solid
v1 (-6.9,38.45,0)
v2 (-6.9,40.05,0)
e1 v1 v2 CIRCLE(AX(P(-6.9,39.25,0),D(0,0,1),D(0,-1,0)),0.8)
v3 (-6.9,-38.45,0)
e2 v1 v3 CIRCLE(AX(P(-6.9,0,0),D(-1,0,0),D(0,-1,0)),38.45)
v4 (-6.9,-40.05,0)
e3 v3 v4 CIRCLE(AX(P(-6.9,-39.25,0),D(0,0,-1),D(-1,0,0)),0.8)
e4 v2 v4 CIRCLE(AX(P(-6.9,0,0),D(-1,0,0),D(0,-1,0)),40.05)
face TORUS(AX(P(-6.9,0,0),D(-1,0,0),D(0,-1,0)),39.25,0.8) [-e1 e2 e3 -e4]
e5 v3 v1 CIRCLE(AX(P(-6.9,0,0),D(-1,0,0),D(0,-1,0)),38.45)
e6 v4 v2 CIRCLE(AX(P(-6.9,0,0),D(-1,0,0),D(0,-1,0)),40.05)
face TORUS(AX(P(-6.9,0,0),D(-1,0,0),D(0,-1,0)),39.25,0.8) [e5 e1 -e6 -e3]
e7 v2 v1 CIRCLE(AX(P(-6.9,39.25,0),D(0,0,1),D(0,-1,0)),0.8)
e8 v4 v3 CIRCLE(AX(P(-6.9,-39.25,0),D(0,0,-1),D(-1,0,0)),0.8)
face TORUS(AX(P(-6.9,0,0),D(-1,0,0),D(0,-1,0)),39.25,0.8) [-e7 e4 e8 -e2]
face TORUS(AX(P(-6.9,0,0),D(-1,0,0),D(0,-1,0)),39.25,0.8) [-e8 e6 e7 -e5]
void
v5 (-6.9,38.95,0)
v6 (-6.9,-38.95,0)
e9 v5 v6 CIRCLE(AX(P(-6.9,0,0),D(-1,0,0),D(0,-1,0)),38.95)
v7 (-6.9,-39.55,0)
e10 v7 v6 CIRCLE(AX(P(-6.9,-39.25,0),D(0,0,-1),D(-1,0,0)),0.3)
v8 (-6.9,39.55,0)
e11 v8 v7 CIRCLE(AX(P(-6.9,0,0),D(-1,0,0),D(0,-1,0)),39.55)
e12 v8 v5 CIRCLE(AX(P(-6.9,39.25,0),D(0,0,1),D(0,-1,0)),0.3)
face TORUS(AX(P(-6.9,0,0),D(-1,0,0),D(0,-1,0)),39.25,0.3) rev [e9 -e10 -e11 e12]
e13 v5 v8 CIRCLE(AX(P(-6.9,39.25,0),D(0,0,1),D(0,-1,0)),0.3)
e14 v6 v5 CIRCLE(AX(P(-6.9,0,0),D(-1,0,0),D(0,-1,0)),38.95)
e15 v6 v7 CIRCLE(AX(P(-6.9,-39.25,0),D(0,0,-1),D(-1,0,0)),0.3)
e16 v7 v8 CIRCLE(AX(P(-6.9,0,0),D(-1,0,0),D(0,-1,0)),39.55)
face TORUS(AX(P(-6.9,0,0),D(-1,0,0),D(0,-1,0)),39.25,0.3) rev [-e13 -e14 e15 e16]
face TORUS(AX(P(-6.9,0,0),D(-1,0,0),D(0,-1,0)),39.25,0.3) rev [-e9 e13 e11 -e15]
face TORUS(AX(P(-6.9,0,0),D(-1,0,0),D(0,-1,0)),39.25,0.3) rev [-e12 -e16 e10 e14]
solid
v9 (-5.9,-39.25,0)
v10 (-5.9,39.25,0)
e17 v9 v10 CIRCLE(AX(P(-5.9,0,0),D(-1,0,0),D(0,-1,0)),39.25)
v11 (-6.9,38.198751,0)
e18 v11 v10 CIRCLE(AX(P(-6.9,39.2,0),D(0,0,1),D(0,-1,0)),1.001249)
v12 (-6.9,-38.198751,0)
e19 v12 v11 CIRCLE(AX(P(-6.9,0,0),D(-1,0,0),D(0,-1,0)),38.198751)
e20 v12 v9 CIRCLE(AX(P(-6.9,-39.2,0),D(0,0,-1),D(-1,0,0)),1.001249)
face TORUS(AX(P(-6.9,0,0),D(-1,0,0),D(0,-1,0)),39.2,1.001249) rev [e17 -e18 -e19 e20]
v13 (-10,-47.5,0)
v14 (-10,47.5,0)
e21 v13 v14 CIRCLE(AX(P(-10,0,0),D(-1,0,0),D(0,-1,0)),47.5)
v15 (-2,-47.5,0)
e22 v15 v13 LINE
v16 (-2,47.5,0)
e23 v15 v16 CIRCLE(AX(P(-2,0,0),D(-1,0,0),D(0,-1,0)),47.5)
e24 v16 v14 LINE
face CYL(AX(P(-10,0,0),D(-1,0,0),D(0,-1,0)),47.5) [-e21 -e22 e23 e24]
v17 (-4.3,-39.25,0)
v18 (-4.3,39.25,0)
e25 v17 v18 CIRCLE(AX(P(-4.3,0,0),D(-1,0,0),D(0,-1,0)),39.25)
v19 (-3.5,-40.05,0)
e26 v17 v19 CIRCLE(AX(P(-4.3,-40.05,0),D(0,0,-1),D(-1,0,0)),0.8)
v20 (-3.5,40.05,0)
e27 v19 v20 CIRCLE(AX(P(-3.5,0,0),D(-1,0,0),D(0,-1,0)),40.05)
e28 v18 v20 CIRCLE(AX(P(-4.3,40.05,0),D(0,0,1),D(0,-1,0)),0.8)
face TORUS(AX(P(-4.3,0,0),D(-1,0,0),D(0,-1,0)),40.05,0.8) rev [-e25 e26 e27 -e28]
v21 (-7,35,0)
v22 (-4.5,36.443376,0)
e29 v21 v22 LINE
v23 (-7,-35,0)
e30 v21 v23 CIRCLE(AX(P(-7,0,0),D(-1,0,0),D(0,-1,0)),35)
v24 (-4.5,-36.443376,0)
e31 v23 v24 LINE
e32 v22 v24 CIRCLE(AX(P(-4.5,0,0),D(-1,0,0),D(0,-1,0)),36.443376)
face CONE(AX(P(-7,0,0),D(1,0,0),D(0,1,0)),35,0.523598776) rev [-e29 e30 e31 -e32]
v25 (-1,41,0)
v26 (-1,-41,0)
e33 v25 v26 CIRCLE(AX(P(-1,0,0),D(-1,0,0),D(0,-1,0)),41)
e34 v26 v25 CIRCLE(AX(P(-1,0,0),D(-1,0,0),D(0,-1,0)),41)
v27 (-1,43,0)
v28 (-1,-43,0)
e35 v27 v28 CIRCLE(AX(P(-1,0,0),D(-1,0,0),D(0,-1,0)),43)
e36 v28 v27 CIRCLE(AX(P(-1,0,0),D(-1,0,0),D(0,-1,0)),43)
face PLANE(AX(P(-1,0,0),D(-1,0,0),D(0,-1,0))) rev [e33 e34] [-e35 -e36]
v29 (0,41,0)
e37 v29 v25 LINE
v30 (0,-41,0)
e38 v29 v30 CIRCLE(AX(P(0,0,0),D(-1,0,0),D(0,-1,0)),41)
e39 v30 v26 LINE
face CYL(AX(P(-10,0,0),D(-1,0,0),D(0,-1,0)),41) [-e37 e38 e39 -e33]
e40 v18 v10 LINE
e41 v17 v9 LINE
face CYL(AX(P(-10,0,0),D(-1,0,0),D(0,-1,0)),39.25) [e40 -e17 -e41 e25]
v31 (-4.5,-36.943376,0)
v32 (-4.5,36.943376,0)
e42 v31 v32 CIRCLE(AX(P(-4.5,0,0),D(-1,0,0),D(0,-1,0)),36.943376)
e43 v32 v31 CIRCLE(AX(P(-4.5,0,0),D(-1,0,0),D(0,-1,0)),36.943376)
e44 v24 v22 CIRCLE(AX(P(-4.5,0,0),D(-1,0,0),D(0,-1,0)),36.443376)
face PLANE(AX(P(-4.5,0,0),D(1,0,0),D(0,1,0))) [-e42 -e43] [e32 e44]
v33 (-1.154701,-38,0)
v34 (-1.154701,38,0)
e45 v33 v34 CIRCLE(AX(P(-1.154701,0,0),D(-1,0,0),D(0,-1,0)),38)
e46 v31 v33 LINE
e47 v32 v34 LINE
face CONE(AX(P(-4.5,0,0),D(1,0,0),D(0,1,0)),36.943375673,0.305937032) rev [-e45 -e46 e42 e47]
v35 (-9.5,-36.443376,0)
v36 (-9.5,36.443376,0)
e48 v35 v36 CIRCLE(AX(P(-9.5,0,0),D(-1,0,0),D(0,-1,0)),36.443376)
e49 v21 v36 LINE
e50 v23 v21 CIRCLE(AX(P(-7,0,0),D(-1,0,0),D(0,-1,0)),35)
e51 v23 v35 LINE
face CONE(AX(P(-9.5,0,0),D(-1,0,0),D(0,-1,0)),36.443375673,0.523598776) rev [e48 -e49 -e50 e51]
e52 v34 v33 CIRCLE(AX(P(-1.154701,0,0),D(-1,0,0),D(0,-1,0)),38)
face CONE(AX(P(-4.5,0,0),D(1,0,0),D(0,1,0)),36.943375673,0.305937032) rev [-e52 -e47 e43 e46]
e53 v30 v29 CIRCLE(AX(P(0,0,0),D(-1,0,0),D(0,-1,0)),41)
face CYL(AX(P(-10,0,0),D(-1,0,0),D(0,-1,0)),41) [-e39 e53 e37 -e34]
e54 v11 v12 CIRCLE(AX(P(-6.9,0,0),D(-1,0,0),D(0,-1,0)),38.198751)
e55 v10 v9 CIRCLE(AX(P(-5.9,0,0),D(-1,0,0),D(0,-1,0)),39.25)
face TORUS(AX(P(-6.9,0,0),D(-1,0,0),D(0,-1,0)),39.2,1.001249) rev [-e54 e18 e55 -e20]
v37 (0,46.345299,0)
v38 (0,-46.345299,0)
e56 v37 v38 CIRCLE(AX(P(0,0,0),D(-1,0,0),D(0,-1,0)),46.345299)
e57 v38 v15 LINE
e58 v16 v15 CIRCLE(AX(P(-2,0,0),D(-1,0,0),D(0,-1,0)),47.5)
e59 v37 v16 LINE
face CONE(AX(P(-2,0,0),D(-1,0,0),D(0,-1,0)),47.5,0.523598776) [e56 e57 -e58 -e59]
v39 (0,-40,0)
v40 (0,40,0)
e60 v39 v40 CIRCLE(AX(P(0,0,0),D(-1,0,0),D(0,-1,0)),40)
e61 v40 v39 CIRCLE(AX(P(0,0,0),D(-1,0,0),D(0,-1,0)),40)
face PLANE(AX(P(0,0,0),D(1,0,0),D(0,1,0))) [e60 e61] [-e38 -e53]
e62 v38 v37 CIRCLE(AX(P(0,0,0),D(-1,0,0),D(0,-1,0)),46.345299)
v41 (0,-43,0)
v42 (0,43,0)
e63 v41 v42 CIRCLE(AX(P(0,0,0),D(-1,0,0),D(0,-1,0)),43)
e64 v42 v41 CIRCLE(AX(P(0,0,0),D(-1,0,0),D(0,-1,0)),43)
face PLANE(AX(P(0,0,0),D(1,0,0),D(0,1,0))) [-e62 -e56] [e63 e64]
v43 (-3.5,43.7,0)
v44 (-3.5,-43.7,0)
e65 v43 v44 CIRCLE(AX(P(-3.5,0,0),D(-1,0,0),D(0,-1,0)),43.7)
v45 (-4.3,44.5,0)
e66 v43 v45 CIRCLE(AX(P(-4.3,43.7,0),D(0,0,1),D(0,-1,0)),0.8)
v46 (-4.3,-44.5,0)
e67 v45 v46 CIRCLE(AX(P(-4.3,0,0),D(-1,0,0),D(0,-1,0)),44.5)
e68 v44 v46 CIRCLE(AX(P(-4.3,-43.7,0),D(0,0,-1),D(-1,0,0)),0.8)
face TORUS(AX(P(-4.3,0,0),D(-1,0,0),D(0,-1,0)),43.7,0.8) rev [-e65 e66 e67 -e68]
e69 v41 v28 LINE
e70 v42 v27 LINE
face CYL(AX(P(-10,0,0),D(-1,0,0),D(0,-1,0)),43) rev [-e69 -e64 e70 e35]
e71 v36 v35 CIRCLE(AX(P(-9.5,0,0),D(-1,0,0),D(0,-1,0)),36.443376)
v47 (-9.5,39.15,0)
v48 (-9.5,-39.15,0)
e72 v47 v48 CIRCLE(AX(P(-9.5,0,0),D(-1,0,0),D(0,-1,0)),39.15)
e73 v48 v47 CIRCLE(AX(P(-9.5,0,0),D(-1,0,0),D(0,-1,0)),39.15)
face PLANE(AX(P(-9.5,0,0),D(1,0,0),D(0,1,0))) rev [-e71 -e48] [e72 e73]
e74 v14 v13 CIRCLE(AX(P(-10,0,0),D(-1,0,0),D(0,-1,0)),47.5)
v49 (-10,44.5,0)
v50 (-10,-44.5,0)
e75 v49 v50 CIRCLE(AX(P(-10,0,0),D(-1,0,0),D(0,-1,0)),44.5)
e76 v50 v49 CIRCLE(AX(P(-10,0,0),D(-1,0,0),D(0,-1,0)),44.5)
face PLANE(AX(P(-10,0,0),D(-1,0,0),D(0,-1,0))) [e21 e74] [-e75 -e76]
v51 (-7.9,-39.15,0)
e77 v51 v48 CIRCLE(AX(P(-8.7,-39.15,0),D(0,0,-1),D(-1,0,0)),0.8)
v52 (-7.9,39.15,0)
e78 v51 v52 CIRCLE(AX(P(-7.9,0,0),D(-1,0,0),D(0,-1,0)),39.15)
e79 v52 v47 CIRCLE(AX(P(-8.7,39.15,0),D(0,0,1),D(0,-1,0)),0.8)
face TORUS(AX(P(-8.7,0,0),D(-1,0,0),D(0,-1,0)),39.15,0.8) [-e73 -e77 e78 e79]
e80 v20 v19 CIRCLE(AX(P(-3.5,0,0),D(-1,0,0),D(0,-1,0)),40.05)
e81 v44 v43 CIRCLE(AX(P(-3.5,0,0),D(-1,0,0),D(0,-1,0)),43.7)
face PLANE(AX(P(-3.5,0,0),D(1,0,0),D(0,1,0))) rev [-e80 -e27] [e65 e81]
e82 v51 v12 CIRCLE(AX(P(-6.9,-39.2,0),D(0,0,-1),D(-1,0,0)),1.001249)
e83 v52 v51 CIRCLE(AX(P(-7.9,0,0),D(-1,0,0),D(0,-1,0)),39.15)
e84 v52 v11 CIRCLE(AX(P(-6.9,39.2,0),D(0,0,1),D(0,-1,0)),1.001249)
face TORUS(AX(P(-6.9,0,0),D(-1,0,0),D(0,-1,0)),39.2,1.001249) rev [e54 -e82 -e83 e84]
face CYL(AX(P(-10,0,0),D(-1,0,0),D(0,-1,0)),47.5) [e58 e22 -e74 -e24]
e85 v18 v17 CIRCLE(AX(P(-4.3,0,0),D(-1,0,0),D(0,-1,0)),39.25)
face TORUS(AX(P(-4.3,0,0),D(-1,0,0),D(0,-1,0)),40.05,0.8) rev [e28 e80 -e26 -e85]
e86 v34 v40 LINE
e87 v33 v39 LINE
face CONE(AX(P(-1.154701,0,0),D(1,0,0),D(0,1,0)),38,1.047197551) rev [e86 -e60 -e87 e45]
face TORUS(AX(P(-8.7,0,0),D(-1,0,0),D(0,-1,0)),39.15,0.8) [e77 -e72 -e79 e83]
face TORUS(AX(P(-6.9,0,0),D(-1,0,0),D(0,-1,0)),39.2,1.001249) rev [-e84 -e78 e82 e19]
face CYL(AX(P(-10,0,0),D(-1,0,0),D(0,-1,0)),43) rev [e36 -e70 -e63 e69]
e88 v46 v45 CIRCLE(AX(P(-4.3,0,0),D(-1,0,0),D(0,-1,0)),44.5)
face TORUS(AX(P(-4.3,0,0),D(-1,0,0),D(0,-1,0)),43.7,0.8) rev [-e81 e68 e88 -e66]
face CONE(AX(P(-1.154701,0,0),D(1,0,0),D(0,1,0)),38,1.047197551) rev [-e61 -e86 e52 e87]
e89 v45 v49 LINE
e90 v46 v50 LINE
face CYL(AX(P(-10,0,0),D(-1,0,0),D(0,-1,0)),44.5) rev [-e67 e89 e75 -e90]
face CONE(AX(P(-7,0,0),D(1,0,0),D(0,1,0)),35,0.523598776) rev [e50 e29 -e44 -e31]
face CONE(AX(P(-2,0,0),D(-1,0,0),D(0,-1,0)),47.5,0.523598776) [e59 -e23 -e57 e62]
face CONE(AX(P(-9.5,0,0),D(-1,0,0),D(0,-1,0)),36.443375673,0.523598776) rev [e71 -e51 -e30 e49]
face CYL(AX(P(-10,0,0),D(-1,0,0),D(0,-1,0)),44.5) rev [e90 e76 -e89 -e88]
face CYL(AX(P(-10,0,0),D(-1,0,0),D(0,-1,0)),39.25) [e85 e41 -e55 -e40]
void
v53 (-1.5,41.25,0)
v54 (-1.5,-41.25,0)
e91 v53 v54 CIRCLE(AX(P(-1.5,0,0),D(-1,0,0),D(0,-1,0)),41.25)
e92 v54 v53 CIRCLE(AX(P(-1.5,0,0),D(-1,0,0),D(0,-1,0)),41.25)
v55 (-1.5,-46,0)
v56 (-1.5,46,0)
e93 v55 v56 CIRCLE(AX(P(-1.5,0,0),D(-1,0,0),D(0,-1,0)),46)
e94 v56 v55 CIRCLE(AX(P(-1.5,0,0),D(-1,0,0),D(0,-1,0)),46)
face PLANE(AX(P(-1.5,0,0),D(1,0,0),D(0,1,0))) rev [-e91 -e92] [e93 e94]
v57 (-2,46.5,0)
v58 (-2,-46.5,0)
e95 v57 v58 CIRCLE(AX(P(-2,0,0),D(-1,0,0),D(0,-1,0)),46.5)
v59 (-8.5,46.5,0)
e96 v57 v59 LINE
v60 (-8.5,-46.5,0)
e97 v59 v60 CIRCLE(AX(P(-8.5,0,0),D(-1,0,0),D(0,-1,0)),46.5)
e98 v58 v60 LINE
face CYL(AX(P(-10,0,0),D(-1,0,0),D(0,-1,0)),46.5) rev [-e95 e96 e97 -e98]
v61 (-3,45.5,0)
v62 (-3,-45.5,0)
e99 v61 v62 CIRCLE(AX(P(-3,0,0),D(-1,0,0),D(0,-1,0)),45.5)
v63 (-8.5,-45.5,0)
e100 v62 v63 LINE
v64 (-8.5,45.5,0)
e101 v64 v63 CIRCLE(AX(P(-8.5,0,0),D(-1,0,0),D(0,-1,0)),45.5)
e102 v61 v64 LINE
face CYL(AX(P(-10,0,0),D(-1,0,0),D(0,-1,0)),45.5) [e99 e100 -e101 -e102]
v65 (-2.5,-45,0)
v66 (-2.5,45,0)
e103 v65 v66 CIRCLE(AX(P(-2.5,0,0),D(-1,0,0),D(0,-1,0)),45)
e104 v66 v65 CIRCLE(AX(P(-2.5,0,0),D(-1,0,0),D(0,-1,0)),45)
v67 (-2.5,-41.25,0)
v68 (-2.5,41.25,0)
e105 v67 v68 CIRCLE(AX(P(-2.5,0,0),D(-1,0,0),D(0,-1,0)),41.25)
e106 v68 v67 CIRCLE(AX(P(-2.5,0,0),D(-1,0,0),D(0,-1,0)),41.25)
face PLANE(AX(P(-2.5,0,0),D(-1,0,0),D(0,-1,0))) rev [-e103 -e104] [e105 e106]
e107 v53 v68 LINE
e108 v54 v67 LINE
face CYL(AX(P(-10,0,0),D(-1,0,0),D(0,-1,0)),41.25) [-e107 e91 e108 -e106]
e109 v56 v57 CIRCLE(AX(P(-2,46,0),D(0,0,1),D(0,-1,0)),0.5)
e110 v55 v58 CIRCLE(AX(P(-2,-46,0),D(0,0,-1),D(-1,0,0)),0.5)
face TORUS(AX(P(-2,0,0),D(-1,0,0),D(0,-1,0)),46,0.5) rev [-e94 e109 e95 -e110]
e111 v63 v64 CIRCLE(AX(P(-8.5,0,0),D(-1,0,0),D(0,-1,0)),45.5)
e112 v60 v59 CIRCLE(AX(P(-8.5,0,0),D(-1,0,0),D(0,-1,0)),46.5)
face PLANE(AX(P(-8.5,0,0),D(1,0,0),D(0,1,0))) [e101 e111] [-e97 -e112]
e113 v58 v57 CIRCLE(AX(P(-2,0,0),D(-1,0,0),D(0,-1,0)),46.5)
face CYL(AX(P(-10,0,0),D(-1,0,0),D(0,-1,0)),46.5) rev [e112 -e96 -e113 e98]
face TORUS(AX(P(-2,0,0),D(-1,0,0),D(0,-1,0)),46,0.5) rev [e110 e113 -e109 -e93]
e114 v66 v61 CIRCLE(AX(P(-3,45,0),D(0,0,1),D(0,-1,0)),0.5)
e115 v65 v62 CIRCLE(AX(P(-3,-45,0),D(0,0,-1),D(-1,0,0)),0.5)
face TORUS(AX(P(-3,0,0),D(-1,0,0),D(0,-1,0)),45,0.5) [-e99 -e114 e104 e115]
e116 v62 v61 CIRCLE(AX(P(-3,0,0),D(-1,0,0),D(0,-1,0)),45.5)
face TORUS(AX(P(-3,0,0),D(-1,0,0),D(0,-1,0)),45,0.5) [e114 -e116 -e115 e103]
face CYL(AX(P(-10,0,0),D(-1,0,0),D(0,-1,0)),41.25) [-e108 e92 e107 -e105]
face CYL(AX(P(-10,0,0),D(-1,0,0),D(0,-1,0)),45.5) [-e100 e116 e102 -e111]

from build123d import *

# Parameters (mm, degrees)
SKETCH_1_R   = 0.8
SKETCH_1_R_2 = 0.3


with BuildPart() as part:
    # 草图1 → 旋转1 (revolve)
    with BuildSketch(Plane.XY, mode=Mode.PRIVATE) as revolve_1_sk:
        with BuildLine():
            ThreePointArc((-7.9, 39.15), (-6.85, 38.2), (-5.9, 39.25))
            Line((-5.9, 39.25), (-4.3, 39.25))
            ThreePointArc((-4.3, 39.25), (-3.734314575, 39.484314575), (-3.5, 40.05))
            Line((-3.5, 40.05), (-3.5, 43.7))
            ThreePointArc((-3.5, 43.7), (-3.734314575, 44.265685425), (-4.3, 44.5))
            Line((-4.3, 44.5), (-10, 44.5))
            Line((-10, 44.5), (-10, 47.5))
            Line((-10, 47.5), (-2, 47.5))
            Line((-2, 47.5), (0, 46.345299462))
            Line((0, 46.345299462), (0, 43))
            Line((0, 43), (-1, 43))
            Line((-1, 43), (-1, 41))
            Line((-1, 41), (0, 41))
            Line((0, 41), (0, 40))
            Line((0, 40), (-1.154700538, 38))
            Line((-1.154700538, 38), (-4.5, 36.943375673))
            Line((-4.5, 36.943375673), (-4.5, 36.443375673))
            Line((-4.5, 36.443375673), (-7, 35))
            Line((-7, 35), (-9.5, 36.443375673))
            Line((-9.5, 36.443375673), (-9.5, 39.15))
            ThreePointArc((-9.5, 39.15), (-8.7, 39.95), (-7.9, 39.15))
        make_face()
        with BuildLine():
            Line((-2.5, 41.25), (-2.5, 45))
            ThreePointArc((-2.5, 45), (-2.646446609, 45.353553391), (-3, 45.5))
            Line((-3, 45.5), (-8.5, 45.5))
            Line((-8.5, 45.5), (-8.5, 46.5))
            Line((-8.5, 46.5), (-2, 46.5))
            ThreePointArc((-2, 46.5), (-1.646446609, 46.353553391), (-1.5, 46))
            Line((-1.5, 46), (-1.5, 41.25))
            Line((-1.5, 41.25), (-2.5, 41.25))
        make_face(mode=Mode.SUBTRACT)
        with Locations((-6.9, 39.25)):
            Circle(SKETCH_1_R)
        with Locations((-6.9, 39.25)):
            Circle(SKETCH_1_R_2, mode=Mode.SUBTRACT)
    revolve(revolve_1_sk.sketch.rotate(Axis((-10, 0, 0), (1, 0, 0)), 180), axis=Axis((-10, 0, 0), (1, 0, 0)))


solid = part.part
